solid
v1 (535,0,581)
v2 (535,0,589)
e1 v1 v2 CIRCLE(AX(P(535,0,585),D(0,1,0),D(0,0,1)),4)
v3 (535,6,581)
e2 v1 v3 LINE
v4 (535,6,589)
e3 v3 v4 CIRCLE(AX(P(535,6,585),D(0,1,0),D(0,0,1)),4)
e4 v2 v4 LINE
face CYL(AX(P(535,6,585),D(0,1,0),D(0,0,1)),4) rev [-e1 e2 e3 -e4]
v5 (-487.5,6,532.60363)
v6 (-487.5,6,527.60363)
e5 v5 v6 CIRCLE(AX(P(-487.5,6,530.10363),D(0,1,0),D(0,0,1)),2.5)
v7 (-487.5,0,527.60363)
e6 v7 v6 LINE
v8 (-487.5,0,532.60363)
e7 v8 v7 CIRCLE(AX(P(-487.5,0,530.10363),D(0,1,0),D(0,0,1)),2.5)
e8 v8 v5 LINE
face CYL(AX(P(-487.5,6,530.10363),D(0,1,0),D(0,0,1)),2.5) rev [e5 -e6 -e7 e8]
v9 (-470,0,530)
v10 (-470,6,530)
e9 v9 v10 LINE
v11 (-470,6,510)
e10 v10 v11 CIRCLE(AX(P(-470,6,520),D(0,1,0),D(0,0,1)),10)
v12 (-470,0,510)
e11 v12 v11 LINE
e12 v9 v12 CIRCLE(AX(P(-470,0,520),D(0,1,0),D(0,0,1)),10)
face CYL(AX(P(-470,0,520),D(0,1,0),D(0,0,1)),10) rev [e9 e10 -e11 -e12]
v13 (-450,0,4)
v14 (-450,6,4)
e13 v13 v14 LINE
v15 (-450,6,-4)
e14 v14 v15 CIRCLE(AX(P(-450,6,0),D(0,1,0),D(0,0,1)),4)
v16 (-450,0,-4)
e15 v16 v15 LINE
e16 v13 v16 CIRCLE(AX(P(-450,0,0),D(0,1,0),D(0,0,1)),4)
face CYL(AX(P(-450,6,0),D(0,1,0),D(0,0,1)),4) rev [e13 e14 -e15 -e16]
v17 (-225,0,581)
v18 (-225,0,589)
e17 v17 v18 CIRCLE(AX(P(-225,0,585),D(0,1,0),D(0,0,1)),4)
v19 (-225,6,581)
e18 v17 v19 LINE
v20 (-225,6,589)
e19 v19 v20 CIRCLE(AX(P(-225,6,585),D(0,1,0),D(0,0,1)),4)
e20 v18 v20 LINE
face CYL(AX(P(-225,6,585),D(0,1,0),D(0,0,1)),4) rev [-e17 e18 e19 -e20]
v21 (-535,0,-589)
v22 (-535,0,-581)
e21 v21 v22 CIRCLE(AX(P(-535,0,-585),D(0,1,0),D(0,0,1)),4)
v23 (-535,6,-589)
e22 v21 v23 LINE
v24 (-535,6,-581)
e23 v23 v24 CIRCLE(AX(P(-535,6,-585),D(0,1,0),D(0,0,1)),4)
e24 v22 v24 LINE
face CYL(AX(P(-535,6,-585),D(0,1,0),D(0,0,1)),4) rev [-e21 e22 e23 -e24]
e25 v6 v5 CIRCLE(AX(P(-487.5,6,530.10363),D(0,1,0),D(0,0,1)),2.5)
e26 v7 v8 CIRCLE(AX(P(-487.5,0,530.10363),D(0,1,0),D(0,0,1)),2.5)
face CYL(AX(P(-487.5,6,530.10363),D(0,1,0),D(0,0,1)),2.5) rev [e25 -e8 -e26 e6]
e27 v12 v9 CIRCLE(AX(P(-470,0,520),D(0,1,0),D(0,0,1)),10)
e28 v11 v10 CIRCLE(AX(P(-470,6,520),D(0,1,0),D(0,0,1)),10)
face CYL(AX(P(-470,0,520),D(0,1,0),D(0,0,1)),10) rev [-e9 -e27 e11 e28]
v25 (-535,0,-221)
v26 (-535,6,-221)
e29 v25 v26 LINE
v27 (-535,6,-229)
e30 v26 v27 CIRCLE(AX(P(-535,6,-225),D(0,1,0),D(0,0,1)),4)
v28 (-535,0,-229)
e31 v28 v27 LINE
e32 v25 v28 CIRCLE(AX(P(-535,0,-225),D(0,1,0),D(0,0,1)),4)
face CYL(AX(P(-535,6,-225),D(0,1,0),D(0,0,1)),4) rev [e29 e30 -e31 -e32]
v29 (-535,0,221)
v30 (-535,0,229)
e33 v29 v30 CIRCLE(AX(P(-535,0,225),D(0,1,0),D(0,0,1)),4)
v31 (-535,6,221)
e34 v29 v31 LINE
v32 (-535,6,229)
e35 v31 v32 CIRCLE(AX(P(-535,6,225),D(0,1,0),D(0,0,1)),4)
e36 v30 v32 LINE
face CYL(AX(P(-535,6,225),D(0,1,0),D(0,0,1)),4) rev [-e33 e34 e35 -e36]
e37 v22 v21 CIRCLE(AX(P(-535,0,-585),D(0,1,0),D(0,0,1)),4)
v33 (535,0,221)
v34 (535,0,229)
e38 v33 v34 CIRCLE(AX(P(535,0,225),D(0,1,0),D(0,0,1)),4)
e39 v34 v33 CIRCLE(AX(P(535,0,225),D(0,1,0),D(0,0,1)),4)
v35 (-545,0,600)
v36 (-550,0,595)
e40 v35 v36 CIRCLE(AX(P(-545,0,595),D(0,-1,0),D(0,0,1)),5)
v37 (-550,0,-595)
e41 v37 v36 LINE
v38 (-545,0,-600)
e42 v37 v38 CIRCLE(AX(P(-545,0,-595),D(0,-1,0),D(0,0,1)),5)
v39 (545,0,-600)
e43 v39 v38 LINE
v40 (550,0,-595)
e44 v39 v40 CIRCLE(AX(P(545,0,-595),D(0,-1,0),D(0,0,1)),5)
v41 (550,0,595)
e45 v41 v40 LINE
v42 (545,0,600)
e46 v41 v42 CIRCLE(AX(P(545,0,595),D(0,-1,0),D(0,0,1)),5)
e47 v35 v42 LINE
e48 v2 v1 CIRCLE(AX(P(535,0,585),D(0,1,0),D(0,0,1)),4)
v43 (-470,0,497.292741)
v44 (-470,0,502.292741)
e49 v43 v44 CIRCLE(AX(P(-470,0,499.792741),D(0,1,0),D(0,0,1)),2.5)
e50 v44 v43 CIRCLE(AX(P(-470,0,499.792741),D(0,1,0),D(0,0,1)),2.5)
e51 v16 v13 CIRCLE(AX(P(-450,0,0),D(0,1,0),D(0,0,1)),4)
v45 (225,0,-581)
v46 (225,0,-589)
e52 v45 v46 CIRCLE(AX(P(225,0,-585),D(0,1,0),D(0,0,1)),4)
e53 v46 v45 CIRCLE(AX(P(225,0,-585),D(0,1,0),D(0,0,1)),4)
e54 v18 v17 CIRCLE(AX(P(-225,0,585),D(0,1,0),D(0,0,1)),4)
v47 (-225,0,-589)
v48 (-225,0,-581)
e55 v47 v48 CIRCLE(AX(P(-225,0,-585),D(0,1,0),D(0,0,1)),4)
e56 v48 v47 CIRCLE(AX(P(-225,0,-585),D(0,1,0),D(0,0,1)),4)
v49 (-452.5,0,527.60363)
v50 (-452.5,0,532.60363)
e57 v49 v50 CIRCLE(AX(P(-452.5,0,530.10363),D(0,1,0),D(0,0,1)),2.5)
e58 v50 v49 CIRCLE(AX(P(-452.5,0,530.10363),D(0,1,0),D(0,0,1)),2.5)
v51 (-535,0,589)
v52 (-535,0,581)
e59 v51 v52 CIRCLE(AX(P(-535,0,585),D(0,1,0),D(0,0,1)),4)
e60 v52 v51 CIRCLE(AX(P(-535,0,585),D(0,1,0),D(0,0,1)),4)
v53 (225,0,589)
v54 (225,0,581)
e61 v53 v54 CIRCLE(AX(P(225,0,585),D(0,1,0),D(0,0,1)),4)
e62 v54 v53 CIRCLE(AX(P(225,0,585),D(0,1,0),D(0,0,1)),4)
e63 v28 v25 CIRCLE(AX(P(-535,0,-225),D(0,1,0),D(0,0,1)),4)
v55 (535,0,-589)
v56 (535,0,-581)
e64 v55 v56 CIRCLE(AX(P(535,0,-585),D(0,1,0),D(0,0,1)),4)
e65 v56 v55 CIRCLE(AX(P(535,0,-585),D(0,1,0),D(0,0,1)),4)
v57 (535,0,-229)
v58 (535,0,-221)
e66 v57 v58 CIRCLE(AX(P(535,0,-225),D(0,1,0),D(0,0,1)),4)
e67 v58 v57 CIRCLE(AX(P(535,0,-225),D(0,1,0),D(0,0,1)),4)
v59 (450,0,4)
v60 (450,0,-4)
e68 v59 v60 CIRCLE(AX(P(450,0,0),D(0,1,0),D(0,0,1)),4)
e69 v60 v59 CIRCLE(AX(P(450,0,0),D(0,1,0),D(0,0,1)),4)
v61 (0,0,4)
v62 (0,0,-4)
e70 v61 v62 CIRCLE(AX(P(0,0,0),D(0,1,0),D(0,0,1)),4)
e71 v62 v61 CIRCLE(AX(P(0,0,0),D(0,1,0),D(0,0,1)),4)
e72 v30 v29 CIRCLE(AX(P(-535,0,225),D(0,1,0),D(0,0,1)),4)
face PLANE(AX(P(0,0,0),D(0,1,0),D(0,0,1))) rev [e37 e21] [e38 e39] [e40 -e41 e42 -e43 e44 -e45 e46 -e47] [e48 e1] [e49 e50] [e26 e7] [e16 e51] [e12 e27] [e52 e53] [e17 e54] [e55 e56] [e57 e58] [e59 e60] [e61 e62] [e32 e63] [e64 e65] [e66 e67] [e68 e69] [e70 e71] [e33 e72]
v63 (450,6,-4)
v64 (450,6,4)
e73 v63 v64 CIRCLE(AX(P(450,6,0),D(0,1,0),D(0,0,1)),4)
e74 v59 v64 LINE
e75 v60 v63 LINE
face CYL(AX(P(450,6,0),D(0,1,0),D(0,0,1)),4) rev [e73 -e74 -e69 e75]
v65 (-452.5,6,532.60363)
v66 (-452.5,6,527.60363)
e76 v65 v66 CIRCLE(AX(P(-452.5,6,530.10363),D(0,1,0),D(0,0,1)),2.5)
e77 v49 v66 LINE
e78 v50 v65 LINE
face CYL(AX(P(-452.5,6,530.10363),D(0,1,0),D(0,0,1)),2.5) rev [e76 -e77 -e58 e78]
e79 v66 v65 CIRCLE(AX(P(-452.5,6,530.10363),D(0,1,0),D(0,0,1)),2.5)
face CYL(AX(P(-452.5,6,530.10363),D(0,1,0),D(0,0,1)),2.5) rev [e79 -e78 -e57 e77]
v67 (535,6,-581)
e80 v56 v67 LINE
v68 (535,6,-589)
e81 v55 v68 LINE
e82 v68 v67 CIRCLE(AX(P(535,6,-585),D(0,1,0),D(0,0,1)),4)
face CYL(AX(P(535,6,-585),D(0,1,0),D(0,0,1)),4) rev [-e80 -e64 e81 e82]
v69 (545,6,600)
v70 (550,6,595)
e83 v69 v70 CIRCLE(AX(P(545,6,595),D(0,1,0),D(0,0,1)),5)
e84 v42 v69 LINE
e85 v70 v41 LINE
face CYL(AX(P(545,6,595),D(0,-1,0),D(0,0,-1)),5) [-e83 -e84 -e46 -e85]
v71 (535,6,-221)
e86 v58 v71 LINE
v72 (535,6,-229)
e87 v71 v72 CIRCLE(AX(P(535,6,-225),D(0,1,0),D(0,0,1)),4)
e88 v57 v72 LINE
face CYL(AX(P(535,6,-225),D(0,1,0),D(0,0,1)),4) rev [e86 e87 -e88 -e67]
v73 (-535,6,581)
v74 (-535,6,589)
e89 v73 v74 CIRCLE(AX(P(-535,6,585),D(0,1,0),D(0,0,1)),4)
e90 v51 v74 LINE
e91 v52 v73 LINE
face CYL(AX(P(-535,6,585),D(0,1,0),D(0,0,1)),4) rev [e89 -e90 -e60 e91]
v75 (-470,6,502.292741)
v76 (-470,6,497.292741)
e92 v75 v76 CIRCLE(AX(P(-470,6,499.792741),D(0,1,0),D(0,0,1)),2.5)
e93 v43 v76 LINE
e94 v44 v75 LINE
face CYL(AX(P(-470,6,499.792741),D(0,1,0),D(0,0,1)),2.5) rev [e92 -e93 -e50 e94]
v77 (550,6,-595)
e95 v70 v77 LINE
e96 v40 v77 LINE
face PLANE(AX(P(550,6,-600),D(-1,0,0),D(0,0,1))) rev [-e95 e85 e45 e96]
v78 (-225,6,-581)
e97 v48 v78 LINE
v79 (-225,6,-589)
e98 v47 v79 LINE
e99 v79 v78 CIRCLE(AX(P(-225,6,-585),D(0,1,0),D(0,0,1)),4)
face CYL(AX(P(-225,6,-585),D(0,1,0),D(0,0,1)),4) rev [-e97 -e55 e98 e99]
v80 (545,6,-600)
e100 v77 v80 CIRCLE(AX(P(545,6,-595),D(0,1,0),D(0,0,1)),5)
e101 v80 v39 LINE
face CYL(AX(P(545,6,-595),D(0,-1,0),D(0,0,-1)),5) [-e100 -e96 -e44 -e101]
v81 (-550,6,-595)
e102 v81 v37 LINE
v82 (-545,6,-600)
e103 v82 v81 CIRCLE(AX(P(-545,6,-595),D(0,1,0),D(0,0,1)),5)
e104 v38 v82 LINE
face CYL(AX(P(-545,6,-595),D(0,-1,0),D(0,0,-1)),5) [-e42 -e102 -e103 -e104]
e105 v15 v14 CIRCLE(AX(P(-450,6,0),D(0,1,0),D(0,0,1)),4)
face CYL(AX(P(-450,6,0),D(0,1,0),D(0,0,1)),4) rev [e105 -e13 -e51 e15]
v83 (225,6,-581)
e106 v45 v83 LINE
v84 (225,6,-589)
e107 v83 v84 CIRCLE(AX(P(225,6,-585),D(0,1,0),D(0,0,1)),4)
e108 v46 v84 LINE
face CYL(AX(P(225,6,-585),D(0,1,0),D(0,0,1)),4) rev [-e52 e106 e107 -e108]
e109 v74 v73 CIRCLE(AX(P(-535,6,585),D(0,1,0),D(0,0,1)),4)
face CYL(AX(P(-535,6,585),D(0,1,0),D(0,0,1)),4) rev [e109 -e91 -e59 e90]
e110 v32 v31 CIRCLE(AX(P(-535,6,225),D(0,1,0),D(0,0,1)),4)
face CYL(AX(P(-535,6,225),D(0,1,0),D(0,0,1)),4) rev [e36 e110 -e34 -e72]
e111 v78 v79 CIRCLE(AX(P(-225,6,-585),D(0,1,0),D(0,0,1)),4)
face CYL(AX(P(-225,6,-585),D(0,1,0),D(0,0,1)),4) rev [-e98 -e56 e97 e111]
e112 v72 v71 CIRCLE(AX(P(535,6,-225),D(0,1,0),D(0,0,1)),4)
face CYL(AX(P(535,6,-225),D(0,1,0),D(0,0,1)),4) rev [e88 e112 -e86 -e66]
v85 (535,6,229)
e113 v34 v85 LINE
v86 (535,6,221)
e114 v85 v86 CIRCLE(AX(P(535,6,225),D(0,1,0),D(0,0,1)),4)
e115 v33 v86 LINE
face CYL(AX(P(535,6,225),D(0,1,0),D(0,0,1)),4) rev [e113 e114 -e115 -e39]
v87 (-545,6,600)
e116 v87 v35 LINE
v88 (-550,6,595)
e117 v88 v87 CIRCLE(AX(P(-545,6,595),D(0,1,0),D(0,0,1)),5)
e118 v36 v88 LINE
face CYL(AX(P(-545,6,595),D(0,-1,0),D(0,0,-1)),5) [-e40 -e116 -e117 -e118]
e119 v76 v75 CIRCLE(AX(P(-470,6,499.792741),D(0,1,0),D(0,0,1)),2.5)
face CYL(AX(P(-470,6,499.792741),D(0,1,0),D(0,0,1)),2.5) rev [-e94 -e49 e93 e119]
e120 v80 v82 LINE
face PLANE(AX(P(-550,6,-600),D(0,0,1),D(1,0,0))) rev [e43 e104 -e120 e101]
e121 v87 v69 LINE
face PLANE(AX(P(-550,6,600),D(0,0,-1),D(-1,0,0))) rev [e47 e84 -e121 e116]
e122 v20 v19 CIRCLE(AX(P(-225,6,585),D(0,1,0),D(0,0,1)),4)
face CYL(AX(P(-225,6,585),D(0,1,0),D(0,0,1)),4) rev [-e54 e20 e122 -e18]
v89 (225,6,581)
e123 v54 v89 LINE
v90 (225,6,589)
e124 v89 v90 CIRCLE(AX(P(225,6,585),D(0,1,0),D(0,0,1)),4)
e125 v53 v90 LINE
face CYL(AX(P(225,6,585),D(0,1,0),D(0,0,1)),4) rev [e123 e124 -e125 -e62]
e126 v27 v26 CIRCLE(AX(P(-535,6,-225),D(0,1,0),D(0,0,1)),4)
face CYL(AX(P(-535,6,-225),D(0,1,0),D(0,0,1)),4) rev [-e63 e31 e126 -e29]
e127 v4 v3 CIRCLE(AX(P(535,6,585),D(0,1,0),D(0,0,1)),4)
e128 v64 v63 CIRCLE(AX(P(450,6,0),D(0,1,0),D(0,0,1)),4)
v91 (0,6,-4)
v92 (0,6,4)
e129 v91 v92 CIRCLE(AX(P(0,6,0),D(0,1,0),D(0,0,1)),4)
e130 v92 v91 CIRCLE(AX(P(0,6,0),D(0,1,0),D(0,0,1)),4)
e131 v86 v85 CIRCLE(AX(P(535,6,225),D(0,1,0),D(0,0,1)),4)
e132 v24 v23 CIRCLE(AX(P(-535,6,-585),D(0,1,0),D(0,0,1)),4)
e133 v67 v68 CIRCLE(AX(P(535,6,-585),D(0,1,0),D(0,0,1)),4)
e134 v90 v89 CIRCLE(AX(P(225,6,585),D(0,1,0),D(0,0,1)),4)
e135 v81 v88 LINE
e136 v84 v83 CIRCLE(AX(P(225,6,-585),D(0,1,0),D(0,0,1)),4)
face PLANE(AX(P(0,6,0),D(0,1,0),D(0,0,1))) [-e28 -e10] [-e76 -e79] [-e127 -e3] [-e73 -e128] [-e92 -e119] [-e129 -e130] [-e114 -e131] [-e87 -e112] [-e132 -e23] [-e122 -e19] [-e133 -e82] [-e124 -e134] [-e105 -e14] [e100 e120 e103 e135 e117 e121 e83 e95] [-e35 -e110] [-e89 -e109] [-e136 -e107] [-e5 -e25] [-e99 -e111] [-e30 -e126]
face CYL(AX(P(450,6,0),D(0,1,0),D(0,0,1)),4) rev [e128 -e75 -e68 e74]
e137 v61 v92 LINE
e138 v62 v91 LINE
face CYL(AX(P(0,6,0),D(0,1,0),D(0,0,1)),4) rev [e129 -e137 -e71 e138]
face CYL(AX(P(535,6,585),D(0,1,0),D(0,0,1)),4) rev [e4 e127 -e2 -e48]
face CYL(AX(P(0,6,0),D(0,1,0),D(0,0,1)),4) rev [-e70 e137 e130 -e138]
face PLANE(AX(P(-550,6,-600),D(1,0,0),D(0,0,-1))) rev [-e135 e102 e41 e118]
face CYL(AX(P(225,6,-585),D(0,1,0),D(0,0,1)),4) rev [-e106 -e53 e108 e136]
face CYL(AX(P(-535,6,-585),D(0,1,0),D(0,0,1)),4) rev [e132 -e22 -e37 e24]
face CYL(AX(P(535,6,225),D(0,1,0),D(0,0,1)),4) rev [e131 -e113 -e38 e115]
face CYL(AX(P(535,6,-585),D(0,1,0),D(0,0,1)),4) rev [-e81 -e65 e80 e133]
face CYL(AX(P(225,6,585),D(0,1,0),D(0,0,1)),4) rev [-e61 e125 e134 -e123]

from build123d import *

# Parameters (mm, degrees)
SKETCH_1_W            = 1100
SKETCH_1_H            = 1200
EXTRUDE_1_DEPTH       = 6
FILLET_1_R            = 5
HOLE_WIZARD_8_0_8_1_D = 8
SKETCH_4_R            = 10
CUT_EXTRUDE_1_DEPTH   = 814.963144129
HOLE_WIZARD_5_0_5_1_D = 5


with BuildPart() as part:
    # 草图1 → 凸台-拉伸1 (new body)
    with BuildSketch(Plane(origin=(0, 0, 0), x_dir=(1, 0, 0), z_dir=(0, 1, 0))):
        Rectangle(SKETCH_1_W, SKETCH_1_H)
    extrude(amount=EXTRUDE_1_DEPTH)

    # 圆角1
    fillet_1_edges = [part.edges().sort_by_distance(p)[0] for p in [
        (550, 3, 600),
        (-550, 3, 600),
        (-550, 3, -600),
        (550, 3, -600),
    ]]
    fillet(fillet_1_edges, radius=FILLET_1_R)

    # Ø8.0 (8) 直径孔1 (through all)
    with Locations(Plane(origin=(0, 6, 0), x_dir=(1, 0, 0), z_dir=(0, 1, 0))):
        with Locations((-535, 585), (535, 585), (-535, -585), (535, -585), (-225, -585), (225, -585), (0, 0), (-225, 585), (225, 585), (-535, -225), (-535, 225), (535, 225), (535, -225), (-450, 0), (450, 0)):
            Hole(HOLE_WIZARD_8_0_8_1_D / 2)

    # 草图4 → 切除-拉伸1 (cut, through all)
    with BuildSketch(Plane(origin=(0, 6, 0), x_dir=(1, 0, 0), z_dir=(0, 1, 0))):
        with Locations(Location((-470, -520, 0), (0, 0, 270))):
            Circle(SKETCH_4_R)
    extrude(amount=-CUT_EXTRUDE_1_DEPTH, mode=Mode.SUBTRACT)

    # Ø5.0 (5) 直径孔1 (through all)
    with Locations(Plane(origin=(0, 6, 0), x_dir=(1, 0, 0), z_dir=(0, 1, 0))):
        with Locations((-470, -499.792740578), (-452.5, -530.103629711), (-487.5, -530.103629711)):
            Hole(HOLE_WIZARD_5_0_5_1_D / 2)


solid = part.part
